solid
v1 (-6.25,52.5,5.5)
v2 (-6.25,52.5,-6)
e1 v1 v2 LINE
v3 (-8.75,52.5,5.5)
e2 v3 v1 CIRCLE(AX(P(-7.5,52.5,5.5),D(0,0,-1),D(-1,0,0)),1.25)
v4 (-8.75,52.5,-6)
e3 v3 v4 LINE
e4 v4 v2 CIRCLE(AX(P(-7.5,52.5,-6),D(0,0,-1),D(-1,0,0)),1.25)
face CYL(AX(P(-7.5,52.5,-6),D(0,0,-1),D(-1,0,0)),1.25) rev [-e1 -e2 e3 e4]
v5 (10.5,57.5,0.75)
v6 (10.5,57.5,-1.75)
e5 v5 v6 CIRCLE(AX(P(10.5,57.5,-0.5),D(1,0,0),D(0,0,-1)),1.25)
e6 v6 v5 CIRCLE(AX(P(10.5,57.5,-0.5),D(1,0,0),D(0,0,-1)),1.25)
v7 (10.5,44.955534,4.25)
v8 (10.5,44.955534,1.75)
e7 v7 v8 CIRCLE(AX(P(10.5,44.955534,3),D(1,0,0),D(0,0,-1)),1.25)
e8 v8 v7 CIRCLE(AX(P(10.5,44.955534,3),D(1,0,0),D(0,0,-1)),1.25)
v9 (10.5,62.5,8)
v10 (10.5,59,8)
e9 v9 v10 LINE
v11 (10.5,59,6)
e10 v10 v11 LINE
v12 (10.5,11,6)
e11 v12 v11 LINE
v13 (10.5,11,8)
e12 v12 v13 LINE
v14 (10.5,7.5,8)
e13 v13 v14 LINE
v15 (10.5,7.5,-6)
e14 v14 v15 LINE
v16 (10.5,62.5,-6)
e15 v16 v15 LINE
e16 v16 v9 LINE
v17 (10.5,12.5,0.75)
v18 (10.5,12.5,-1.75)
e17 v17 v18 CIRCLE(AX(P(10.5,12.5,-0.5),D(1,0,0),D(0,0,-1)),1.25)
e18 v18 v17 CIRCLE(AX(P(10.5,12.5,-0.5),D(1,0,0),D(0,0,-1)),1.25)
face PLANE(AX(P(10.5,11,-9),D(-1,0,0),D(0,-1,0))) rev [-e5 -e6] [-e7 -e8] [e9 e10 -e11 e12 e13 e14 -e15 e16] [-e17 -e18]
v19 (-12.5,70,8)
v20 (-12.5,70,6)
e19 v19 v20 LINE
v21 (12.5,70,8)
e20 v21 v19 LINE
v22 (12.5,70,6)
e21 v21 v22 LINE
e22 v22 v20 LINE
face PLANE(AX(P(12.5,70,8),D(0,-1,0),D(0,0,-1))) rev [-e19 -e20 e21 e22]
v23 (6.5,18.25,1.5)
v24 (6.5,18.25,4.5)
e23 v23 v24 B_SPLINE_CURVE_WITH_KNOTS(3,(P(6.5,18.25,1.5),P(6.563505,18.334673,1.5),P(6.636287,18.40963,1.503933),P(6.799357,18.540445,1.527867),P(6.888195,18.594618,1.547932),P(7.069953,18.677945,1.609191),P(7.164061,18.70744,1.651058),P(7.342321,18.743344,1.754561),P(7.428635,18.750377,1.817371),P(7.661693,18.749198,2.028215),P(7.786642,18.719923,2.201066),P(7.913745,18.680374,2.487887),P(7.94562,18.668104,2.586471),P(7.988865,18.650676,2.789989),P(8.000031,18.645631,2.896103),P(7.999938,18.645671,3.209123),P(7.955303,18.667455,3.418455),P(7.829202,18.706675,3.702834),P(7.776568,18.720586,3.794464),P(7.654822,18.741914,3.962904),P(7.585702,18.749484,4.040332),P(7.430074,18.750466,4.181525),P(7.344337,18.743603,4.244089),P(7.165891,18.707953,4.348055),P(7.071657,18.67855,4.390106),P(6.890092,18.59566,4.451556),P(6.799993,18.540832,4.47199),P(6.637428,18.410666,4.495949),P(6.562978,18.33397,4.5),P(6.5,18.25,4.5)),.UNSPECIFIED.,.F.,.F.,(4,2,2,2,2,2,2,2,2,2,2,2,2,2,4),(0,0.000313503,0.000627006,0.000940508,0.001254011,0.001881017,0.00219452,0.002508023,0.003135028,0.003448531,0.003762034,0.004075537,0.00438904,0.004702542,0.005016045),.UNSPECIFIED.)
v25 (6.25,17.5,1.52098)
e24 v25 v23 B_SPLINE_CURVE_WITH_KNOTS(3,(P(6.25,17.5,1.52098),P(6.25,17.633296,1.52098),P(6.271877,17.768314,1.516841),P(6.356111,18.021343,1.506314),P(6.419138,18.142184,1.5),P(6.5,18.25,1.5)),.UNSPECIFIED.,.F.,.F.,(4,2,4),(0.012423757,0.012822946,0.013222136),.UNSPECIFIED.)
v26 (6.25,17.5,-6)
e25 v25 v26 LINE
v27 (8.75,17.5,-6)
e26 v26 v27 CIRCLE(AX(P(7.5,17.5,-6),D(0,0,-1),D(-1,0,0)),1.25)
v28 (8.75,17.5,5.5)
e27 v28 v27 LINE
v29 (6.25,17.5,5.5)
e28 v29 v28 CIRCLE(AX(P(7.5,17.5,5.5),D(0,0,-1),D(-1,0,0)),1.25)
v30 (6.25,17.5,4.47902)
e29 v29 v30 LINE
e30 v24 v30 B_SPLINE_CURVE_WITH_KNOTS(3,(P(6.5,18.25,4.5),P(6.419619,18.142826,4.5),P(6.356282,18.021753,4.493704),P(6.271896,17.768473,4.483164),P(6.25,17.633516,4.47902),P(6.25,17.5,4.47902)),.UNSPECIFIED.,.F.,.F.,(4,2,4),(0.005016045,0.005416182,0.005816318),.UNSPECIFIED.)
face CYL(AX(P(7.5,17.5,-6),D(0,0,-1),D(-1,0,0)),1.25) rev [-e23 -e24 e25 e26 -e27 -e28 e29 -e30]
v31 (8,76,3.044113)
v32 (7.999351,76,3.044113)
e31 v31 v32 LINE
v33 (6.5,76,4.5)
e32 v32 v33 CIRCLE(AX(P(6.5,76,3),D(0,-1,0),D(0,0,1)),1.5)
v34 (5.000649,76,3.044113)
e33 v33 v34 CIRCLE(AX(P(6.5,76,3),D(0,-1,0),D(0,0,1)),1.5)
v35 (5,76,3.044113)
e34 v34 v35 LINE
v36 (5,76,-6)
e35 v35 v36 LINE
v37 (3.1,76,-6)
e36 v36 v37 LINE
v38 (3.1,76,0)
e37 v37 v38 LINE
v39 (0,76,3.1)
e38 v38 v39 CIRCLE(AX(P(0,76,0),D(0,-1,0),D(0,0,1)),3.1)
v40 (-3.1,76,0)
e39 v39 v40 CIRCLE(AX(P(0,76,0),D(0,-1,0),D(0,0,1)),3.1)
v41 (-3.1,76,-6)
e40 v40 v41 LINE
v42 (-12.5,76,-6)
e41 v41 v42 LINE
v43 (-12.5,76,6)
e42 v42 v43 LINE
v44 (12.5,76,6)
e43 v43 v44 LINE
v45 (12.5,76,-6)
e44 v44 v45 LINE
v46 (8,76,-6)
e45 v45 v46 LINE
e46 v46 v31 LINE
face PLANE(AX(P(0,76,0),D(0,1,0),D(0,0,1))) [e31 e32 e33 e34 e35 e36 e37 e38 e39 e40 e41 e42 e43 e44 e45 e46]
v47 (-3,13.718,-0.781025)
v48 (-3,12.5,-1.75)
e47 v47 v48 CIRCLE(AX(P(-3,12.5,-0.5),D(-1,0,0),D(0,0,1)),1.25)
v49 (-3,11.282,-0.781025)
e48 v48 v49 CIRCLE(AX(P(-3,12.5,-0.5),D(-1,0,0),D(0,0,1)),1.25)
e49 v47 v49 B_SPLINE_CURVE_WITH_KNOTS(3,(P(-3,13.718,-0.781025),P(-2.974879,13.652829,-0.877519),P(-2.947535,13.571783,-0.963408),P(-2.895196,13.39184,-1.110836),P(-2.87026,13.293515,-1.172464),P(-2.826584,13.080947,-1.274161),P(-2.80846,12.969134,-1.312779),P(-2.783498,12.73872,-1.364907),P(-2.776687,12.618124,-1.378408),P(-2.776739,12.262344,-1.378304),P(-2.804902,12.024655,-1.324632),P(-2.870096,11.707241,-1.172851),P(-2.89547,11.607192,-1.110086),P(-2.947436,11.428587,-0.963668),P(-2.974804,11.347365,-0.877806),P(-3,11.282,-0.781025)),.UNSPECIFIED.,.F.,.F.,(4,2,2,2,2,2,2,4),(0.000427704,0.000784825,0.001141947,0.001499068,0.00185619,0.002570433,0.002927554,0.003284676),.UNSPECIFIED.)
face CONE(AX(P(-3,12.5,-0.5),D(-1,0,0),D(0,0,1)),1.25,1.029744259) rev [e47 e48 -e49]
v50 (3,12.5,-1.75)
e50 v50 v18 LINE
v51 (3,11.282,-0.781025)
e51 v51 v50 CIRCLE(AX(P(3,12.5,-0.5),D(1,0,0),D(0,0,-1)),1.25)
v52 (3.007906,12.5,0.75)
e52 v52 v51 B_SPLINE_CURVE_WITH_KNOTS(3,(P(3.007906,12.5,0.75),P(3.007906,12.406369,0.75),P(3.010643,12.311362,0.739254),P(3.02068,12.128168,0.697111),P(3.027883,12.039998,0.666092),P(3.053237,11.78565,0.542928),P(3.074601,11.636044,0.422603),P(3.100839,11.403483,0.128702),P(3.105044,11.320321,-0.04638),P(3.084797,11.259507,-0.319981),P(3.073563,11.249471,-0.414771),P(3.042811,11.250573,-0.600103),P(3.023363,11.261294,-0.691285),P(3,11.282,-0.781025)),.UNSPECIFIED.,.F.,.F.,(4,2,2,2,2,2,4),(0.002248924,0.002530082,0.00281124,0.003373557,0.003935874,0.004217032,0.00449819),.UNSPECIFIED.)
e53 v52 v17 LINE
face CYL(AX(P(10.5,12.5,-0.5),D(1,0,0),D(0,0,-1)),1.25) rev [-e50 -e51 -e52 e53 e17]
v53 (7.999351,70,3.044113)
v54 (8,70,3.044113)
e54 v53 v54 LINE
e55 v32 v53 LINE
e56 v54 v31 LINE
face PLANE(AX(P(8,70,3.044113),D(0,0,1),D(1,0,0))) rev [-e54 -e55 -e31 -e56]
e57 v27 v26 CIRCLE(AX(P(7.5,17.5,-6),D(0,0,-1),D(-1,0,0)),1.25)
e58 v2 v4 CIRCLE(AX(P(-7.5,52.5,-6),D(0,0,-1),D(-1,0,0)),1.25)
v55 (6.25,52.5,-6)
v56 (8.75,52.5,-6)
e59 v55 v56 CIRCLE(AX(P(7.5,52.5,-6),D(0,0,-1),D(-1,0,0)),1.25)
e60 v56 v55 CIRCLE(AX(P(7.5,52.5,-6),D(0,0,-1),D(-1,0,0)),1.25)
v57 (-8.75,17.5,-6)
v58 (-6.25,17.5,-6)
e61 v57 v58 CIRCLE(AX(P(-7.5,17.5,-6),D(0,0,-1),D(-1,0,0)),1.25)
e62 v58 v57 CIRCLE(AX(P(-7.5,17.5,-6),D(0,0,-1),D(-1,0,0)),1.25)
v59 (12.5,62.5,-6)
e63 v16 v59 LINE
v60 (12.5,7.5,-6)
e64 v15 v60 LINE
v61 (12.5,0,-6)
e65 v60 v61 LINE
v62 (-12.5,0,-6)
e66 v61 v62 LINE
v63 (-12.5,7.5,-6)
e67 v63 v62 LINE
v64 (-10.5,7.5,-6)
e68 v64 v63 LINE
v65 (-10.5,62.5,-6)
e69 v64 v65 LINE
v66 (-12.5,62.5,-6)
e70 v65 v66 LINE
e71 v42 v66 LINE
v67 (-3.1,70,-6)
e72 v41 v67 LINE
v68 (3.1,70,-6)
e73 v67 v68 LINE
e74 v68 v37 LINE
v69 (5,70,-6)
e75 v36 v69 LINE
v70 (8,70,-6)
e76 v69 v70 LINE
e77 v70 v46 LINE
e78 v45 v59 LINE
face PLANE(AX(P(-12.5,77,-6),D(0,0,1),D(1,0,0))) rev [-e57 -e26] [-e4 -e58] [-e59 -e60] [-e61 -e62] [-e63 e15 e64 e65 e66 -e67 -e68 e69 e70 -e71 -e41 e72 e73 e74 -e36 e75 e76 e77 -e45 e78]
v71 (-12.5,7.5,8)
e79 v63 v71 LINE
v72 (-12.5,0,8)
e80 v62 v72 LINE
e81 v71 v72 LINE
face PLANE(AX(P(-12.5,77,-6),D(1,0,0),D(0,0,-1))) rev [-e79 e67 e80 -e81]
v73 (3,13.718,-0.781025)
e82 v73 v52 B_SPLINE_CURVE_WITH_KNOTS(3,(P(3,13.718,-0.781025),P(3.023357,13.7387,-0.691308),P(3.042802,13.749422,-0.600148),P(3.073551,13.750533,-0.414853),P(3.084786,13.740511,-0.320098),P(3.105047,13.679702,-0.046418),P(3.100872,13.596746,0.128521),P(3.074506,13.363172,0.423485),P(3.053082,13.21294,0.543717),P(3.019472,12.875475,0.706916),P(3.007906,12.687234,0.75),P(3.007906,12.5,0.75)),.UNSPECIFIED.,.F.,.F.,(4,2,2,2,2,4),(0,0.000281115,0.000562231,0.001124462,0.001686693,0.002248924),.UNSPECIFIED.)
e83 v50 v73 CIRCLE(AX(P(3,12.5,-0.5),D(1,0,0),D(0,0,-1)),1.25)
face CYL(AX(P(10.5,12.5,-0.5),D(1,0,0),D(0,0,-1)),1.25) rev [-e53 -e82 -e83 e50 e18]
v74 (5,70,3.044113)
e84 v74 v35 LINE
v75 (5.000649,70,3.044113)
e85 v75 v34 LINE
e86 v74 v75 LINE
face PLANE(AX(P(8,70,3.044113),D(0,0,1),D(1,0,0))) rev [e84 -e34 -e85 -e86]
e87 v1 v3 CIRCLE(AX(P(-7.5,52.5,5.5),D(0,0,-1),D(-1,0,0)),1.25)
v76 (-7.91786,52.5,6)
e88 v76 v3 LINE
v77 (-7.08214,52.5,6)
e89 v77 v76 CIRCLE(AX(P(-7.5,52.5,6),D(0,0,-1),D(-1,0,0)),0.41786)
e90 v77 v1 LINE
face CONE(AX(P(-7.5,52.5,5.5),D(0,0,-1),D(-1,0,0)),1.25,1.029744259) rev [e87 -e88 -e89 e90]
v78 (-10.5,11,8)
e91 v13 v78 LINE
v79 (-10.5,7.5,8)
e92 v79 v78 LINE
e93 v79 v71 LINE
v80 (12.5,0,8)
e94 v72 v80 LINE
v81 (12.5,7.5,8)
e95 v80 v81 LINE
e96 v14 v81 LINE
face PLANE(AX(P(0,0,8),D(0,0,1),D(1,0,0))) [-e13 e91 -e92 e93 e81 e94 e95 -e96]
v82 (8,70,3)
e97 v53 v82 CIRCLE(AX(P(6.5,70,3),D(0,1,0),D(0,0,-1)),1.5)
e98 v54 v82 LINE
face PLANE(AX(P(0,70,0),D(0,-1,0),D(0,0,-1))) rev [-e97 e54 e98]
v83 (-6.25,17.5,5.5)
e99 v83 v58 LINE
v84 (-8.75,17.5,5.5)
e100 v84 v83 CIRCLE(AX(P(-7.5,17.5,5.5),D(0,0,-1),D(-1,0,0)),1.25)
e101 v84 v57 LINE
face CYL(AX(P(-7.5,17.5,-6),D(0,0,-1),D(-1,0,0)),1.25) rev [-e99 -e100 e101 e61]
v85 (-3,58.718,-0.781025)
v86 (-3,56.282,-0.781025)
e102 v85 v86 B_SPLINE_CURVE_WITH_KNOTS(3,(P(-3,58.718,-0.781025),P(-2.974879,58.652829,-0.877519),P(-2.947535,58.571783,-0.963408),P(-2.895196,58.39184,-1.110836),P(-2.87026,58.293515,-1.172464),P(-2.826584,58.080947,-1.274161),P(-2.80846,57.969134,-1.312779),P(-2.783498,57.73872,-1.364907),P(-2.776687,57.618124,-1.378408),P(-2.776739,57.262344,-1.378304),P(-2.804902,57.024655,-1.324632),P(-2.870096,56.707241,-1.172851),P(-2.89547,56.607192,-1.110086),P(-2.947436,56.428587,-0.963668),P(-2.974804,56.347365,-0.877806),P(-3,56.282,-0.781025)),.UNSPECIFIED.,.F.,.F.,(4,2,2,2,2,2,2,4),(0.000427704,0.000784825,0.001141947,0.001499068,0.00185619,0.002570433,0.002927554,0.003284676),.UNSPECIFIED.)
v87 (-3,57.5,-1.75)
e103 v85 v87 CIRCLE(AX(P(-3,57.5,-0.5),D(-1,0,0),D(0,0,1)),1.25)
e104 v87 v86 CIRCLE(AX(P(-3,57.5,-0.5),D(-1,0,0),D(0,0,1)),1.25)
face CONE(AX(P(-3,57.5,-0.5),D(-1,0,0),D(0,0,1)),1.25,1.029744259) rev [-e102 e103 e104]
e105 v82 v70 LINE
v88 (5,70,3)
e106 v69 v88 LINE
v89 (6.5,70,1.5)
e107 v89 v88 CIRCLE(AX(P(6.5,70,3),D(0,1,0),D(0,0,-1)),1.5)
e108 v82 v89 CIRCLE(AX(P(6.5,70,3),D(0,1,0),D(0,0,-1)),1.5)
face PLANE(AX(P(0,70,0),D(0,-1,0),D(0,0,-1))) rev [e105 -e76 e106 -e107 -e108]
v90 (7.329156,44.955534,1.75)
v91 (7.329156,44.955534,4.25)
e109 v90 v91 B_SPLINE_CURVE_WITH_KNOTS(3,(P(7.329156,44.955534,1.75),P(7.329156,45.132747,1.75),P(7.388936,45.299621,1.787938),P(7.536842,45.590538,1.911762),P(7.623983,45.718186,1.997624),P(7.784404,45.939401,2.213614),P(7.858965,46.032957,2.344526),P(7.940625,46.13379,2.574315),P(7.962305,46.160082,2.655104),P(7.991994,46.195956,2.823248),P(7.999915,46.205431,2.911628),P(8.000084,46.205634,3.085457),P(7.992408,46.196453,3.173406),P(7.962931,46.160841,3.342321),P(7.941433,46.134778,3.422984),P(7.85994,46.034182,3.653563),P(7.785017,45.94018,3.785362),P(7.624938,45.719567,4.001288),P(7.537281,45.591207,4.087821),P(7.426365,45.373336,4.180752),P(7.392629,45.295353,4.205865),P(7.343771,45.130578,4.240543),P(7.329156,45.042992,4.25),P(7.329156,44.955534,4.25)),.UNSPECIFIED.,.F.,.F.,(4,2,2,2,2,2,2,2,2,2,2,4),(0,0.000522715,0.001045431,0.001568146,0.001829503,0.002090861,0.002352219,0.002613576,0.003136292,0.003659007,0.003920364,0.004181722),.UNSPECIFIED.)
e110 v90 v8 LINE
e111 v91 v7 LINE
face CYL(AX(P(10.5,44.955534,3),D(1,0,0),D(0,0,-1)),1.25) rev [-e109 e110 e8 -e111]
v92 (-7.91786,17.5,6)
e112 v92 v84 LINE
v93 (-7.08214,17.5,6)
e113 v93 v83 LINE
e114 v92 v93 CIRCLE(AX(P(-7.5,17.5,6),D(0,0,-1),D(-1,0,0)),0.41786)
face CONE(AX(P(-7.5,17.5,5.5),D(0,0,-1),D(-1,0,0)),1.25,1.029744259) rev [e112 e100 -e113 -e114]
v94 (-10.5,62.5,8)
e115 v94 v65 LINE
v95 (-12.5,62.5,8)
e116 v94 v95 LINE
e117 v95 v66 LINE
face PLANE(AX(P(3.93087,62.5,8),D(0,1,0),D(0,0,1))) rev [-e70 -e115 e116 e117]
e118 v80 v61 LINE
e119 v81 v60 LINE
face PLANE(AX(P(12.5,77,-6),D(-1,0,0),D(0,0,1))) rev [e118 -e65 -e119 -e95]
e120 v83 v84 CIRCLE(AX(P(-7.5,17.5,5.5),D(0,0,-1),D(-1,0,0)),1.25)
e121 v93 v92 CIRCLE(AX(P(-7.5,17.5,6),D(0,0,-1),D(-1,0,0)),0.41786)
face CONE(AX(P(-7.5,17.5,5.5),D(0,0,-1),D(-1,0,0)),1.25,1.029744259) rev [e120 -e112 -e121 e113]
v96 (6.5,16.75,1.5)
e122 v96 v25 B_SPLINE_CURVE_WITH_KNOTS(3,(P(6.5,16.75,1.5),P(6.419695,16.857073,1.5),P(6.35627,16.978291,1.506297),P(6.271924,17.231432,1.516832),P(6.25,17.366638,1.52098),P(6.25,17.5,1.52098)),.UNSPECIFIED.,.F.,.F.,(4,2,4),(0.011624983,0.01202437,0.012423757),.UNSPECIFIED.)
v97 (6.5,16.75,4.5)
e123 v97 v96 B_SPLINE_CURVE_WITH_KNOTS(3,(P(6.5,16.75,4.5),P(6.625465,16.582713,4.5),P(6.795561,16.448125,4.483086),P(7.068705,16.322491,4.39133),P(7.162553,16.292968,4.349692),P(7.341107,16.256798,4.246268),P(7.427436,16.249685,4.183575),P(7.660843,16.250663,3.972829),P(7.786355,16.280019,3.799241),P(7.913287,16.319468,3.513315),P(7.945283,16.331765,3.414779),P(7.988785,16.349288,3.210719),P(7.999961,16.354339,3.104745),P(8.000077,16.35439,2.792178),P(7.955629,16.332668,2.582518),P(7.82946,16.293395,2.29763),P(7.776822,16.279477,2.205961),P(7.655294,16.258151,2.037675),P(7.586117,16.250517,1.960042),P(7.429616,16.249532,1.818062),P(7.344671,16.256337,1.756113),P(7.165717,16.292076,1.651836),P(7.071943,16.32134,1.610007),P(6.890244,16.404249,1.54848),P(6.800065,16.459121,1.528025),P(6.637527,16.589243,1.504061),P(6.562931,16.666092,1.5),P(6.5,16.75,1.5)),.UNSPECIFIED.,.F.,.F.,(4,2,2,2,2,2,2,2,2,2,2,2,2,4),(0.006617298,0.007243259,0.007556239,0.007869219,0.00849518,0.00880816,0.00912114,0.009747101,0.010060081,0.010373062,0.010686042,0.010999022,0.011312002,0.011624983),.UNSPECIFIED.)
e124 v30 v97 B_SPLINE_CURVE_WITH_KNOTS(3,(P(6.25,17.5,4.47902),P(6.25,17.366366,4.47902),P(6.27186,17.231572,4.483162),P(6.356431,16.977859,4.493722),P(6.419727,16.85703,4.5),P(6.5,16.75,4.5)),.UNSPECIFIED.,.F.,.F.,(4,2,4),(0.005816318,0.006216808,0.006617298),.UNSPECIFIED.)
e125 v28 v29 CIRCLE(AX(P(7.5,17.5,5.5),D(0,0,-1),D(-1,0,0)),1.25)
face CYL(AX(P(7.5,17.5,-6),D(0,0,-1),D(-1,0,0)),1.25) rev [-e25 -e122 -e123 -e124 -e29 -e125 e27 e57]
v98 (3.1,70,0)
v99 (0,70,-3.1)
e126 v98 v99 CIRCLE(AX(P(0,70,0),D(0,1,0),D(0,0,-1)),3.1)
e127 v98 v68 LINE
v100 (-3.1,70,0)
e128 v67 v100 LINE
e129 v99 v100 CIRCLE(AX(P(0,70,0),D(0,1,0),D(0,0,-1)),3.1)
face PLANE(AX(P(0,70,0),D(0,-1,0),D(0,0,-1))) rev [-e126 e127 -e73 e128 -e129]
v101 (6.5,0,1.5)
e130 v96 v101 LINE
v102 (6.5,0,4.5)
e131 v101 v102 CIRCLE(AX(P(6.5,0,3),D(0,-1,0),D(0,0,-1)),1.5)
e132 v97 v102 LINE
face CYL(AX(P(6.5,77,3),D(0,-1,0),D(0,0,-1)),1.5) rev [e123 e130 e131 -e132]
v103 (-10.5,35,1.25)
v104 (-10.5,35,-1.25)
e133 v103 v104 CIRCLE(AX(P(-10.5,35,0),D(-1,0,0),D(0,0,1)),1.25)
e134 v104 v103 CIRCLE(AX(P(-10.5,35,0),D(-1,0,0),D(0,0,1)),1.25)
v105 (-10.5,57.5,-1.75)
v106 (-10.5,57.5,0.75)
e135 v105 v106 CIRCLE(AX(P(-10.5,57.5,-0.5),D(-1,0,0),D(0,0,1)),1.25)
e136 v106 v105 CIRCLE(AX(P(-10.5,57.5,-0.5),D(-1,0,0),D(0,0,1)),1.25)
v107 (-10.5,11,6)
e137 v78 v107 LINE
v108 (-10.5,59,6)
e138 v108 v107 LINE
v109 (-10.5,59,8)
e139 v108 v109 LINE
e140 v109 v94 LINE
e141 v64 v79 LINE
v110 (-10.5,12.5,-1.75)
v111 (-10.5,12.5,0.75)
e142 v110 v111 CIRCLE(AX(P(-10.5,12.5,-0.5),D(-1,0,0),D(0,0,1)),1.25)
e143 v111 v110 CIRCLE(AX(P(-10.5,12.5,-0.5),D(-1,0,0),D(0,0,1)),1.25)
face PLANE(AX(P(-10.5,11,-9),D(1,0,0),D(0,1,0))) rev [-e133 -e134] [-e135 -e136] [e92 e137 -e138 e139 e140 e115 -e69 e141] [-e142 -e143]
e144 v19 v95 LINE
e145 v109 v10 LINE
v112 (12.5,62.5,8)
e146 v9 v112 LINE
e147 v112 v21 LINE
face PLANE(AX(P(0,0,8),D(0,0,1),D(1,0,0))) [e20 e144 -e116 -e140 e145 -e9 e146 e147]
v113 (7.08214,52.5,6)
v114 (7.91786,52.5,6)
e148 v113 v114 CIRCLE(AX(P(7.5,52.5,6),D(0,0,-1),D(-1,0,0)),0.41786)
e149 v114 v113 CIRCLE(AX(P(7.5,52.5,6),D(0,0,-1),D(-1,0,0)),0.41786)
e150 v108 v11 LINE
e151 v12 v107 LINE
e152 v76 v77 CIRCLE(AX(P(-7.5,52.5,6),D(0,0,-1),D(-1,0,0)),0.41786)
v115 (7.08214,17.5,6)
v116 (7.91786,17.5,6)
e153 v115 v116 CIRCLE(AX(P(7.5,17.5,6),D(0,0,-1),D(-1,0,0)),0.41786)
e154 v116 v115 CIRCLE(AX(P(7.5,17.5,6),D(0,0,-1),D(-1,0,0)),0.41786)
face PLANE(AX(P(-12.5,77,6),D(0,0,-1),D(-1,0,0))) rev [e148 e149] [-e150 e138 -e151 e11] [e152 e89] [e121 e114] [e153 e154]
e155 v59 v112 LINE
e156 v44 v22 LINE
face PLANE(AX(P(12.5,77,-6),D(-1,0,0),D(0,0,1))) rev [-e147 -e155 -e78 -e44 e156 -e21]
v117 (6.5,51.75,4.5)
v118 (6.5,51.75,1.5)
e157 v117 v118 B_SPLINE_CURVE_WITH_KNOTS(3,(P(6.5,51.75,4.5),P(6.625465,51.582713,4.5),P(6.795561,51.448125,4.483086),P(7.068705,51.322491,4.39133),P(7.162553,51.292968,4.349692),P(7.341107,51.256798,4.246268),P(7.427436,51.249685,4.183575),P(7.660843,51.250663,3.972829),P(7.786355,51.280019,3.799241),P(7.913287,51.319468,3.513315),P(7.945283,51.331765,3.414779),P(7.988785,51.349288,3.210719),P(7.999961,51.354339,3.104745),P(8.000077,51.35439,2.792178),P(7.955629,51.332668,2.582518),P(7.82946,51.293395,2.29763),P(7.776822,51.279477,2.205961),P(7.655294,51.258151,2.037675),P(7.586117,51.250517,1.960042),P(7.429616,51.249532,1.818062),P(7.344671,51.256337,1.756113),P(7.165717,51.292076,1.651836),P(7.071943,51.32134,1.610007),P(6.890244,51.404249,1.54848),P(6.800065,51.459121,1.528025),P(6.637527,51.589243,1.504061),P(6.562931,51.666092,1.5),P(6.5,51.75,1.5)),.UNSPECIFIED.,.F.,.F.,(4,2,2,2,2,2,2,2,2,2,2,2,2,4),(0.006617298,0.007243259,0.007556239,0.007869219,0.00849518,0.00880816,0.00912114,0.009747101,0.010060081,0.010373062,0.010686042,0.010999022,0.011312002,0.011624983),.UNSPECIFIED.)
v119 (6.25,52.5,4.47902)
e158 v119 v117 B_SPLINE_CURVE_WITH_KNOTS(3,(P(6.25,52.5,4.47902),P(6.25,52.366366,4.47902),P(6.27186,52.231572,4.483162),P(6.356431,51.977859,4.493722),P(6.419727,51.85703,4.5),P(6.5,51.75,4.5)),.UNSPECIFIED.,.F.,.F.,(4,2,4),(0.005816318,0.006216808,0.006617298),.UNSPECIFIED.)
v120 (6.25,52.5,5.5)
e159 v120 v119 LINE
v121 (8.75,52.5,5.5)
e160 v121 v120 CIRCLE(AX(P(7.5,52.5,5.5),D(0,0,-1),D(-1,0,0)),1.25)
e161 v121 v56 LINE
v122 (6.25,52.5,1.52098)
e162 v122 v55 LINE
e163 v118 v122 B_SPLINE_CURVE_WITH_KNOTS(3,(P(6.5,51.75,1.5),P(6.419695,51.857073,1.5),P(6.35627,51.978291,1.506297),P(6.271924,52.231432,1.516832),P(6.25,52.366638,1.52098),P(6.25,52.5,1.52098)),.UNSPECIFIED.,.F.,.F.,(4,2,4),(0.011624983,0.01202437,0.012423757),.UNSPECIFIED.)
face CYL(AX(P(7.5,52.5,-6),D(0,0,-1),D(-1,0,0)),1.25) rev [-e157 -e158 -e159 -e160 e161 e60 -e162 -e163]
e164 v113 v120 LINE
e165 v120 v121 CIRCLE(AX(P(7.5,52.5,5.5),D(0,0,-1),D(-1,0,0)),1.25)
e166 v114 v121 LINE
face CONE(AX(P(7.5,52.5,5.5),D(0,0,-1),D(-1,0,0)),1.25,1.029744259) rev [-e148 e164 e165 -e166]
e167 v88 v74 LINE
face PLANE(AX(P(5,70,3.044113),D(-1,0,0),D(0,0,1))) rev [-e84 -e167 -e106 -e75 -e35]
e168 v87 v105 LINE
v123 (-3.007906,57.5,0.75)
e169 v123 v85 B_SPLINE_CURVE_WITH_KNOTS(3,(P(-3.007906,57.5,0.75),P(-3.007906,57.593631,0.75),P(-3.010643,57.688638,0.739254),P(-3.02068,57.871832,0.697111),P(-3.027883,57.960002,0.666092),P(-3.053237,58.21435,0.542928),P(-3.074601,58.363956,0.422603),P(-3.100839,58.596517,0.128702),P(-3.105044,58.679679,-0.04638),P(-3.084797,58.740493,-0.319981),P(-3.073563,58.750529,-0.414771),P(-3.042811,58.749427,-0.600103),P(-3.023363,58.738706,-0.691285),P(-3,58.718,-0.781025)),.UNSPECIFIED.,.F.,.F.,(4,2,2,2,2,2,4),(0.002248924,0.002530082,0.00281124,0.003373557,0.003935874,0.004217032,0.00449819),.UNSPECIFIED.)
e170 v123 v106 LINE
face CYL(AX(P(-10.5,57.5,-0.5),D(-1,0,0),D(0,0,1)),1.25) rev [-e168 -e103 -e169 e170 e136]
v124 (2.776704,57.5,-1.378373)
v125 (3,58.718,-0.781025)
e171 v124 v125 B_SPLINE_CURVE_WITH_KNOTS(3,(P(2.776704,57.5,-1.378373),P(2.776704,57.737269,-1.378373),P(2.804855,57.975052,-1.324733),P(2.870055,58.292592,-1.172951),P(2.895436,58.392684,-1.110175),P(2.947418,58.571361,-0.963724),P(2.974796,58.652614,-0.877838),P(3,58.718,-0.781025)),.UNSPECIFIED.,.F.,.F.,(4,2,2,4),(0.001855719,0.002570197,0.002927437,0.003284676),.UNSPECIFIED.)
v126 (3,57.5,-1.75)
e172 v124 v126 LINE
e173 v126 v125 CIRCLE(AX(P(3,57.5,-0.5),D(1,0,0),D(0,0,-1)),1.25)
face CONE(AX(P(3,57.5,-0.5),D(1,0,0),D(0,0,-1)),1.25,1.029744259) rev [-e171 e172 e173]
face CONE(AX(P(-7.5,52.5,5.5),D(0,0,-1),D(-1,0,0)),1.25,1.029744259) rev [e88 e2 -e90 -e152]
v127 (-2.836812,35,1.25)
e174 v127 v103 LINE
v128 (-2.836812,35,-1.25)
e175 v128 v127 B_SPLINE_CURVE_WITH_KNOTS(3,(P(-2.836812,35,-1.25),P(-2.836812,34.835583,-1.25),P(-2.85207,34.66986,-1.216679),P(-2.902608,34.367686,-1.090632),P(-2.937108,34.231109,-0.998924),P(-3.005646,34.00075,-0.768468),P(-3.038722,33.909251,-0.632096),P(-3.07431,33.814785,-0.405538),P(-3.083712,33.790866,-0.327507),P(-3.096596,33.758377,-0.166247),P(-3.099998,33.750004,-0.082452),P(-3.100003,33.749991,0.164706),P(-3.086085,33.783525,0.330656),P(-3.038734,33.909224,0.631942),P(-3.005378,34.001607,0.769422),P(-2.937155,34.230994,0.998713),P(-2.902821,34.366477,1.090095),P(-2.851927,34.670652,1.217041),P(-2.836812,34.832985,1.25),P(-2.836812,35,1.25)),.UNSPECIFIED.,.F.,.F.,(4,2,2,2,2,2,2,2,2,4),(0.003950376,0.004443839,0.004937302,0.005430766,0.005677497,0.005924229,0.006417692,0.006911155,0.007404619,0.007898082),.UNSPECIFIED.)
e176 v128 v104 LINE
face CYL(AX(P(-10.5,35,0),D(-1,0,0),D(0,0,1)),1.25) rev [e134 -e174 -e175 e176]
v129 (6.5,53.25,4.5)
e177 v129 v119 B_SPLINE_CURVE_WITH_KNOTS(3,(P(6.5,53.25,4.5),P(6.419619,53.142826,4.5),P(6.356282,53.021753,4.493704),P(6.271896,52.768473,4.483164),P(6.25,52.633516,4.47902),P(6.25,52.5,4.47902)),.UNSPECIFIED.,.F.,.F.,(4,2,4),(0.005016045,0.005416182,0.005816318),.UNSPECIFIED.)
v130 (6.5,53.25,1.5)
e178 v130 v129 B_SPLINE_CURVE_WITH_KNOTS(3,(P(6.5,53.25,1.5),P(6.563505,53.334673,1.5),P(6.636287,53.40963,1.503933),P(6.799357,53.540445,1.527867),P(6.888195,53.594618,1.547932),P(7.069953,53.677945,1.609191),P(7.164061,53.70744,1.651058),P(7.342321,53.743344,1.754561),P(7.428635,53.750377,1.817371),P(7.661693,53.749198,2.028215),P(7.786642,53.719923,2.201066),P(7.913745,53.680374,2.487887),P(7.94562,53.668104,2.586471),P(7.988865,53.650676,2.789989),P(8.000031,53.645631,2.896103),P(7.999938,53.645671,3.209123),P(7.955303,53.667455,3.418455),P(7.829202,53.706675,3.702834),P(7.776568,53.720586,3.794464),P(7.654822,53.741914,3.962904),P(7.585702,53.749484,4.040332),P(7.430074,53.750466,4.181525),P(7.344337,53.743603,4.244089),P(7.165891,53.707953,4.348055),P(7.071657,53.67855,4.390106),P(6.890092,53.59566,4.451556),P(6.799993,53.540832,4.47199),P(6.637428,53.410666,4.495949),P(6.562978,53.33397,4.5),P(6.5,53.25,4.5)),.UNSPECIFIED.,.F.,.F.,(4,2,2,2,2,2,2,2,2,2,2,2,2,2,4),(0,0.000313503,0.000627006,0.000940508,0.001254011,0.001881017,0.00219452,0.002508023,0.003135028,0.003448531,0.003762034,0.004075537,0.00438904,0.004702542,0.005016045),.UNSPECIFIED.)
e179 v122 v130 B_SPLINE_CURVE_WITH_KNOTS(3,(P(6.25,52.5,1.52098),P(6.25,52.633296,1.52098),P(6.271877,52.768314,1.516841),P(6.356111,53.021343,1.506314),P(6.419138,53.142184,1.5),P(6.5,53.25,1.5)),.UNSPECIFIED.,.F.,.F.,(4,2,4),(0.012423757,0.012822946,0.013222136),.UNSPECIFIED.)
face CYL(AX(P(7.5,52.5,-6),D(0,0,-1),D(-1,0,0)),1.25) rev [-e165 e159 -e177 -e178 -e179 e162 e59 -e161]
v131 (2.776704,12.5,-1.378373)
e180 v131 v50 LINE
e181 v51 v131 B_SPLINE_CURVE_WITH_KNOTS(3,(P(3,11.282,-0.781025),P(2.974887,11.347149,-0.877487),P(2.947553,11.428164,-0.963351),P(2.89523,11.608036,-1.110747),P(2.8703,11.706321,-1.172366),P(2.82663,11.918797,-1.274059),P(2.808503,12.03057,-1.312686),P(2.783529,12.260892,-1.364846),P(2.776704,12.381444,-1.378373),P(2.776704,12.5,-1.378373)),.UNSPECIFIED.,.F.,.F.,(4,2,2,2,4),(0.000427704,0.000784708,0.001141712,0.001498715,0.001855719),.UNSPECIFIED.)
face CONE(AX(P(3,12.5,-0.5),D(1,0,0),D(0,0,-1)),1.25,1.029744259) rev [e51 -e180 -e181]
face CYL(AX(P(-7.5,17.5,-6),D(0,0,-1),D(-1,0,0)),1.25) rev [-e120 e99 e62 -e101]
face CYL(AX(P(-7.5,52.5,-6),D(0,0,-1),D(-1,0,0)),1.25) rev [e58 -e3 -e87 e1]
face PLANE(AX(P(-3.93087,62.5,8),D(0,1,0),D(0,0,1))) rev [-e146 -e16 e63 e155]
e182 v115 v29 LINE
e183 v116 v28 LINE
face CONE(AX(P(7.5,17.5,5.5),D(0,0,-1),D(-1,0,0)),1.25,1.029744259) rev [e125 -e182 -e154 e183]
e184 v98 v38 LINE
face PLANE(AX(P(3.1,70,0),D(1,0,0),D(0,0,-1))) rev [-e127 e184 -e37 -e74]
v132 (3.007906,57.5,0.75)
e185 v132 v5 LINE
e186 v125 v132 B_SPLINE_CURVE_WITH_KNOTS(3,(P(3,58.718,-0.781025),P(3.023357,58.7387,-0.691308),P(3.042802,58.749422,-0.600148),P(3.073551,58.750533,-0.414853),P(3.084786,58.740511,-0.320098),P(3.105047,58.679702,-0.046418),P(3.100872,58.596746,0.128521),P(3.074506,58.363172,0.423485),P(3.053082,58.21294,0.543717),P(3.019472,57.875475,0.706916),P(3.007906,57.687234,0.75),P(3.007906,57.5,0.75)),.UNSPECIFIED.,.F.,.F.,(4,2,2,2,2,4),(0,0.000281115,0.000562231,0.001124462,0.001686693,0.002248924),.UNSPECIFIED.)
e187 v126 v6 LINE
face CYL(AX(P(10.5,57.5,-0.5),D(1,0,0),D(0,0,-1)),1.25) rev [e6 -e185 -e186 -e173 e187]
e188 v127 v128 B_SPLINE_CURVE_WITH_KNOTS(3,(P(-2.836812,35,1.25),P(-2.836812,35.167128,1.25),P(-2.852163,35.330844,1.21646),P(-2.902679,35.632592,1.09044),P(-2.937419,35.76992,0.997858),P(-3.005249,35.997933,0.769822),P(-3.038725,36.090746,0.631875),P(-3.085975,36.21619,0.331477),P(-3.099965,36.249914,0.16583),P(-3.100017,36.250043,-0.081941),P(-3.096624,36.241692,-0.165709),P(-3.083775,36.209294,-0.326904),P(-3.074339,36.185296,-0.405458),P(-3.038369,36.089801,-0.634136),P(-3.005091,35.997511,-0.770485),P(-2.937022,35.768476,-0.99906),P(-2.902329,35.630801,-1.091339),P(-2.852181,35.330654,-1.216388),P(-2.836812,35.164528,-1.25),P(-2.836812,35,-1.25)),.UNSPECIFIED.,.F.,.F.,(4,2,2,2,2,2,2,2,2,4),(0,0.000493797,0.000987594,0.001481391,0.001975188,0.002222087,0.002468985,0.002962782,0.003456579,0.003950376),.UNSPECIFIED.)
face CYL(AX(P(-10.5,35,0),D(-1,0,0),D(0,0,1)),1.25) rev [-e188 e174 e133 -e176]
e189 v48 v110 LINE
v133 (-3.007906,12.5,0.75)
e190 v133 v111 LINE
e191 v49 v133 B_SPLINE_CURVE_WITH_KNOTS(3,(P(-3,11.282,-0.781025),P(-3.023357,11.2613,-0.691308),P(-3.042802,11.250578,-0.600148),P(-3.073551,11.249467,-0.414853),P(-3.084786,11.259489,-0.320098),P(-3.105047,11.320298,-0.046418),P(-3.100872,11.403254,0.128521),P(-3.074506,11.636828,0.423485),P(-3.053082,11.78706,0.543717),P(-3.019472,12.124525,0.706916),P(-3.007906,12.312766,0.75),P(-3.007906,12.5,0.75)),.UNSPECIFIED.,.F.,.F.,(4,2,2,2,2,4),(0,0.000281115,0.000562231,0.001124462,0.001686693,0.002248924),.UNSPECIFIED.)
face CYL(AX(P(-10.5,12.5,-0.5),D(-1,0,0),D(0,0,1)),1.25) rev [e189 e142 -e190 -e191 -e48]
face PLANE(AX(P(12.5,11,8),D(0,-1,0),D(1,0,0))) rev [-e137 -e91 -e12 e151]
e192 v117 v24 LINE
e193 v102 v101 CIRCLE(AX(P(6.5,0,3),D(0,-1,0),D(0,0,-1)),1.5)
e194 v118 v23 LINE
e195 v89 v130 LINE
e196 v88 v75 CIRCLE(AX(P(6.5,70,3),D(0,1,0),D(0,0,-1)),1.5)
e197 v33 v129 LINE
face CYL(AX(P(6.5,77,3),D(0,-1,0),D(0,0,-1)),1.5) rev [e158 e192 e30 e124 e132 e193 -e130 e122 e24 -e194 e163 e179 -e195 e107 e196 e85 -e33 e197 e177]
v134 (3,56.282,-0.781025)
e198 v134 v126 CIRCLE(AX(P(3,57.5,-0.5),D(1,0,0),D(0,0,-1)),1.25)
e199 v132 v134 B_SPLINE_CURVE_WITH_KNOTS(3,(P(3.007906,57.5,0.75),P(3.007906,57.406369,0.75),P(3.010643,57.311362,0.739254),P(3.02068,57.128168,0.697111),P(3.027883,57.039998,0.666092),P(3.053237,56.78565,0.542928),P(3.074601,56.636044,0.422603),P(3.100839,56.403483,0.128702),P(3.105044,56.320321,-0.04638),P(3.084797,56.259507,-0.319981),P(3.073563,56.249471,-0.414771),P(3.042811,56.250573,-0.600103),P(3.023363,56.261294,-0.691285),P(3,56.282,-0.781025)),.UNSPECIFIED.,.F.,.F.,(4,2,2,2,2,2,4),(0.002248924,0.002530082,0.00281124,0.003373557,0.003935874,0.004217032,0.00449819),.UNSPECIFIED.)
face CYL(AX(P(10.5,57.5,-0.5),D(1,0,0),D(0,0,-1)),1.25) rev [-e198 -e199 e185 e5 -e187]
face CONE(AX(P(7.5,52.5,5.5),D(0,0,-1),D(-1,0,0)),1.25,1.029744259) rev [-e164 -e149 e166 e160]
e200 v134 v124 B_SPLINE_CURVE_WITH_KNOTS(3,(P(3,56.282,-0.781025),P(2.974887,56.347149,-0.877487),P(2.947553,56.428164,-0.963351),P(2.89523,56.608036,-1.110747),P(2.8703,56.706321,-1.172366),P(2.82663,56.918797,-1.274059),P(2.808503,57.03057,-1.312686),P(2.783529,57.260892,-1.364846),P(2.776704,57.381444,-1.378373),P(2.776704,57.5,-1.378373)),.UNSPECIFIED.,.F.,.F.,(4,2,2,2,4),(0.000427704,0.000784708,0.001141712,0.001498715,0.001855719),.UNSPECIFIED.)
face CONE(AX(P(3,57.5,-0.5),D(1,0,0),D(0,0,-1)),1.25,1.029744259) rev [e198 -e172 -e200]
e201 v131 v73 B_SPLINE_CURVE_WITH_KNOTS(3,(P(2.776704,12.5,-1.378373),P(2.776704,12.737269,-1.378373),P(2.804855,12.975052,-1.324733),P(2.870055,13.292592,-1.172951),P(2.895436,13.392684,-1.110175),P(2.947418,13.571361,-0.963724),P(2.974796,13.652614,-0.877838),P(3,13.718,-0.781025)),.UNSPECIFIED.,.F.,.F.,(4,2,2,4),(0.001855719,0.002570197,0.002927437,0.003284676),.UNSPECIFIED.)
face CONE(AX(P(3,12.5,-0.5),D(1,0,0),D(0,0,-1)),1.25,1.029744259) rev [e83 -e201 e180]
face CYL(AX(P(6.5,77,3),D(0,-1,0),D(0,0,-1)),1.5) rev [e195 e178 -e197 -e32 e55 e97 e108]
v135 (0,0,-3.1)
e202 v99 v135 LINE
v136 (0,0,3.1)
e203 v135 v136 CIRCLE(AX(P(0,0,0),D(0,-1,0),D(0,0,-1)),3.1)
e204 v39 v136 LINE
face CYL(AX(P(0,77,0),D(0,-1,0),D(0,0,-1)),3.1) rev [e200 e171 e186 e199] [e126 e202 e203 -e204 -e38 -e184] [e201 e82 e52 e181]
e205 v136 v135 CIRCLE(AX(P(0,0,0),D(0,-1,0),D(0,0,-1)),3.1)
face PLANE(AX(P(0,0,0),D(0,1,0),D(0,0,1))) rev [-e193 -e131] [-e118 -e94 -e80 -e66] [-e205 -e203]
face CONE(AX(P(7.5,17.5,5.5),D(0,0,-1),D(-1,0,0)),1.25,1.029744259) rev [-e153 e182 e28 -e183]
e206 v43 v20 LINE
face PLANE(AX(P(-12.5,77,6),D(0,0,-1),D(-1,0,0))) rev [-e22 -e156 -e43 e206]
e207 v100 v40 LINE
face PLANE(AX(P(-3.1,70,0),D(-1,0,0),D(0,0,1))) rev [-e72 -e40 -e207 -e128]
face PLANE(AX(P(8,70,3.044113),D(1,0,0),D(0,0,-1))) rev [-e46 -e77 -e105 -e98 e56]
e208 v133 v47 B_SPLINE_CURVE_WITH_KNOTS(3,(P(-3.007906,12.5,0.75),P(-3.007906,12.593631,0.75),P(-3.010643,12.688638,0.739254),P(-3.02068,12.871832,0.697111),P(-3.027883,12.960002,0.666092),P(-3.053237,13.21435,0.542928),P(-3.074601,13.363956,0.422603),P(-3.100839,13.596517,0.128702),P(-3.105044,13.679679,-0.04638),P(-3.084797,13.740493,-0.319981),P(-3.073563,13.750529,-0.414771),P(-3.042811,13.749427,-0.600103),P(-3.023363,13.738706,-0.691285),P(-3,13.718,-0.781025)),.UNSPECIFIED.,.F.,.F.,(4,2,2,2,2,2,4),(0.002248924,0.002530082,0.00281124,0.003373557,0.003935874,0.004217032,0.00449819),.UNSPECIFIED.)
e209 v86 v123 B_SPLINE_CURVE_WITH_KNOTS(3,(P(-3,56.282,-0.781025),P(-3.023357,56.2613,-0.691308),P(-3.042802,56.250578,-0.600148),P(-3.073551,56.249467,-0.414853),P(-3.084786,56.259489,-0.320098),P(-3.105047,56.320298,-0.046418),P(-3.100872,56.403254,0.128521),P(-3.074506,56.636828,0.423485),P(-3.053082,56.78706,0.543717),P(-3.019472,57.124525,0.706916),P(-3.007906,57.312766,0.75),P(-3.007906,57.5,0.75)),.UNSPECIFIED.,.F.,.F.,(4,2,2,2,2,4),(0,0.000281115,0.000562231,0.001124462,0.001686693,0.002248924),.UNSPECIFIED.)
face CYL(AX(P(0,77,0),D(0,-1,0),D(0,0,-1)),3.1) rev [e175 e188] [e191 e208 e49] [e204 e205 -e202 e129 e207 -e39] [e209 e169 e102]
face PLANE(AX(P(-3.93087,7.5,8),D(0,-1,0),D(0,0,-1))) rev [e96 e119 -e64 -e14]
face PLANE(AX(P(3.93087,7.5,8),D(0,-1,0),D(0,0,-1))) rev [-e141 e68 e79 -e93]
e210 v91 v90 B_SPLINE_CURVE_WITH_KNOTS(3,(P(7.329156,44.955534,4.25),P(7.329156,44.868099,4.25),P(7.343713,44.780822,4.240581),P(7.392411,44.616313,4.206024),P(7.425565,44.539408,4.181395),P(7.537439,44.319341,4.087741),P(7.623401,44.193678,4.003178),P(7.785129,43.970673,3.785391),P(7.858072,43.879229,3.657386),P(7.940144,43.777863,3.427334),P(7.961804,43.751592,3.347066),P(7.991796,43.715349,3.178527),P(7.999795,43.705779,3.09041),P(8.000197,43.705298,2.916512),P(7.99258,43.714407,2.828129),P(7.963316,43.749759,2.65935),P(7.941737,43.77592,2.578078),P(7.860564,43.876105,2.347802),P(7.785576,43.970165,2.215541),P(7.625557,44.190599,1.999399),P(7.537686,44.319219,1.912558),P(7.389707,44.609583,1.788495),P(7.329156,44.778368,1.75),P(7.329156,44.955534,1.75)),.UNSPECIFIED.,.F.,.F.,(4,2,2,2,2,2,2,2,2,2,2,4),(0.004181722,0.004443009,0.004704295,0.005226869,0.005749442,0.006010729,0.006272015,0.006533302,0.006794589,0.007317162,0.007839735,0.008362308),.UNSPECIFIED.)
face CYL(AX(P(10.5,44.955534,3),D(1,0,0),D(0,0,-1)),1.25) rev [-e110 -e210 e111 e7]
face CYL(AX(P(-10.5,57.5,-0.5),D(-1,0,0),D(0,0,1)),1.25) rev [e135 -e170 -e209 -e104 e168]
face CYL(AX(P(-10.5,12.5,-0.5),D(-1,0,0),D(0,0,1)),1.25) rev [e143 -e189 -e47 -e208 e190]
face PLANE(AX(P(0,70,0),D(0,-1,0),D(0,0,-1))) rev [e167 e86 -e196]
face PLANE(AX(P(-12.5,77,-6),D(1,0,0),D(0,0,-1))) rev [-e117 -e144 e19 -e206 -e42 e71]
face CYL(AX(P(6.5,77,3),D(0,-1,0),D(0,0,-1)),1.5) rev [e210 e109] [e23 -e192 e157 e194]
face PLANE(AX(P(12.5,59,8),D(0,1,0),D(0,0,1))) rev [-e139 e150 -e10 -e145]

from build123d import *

# Parameters (mm, degrees)
SKETCH1_W                  = 25
SKETCH1_H                  = 12
BOSS_EXTRUDE1_DEPTH        = 77
SKETCH2_R                  = 3.1
SKETCH2_R_2                = 1.5
CUT_EXTRUDE1_DEPTH         = 79.238417673
SKETCH4_W                  = 6.2
SKETCH4_H                  = 12
SKETCH4_W_2                = 3
SKETCH4_H_2                = 18.04411339
CUT_EXTRUDE3_DEPTH         = 7
SKETCH5_W                  = 25
SKETCH5_H                  = 11
BOSS_EXTRUDE2_DEPTH        = 2
SKETCH6_W                  = 2
SKETCH6_H                  = 48
CUT_EXTRUDE4_DEPTH         = 17
M3_TAPPED_HOLE1_AT_2_COUNT = 2
M3_TAPPED_HOLE1_AT_2_PITCH = 45
M3_TAPPED_HOLE2_D          = 2.5
M3_TAPPED_HOLE2_DEPTH      = 11.5
M3_TAPPED_HOLE2_TIP        = 0.751075774
SKETCH13_W                 = 14
SKETCH13_H                 = 3.5
CUT_EXTRUDE5_DEPTH         = 2
SKETCH14_W                 = 14
SKETCH14_H                 = 3.5
CUT_EXTRUDE6_DEPTH         = 2
M3_TAPPED_HOLE3_D          = 2.5
M3_TAPPED_HOLE3_DEPTH      = 4.5
M3_TAPPED_HOLE3_TIP        = 0.751075774
SKETCH20_W                 = 25
SKETCH20_H                 = 14
CUT_EXTRUDE9_DEPTH         = 1
M3_TAPPED_HOLE5_D          = 2.5
M3_TAPPED_HOLE5_DEPTH      = 9
M3_TAPPED_HOLE5_TIP        = 0.751075774


with BuildPart() as part:
    # Sketch1 → Boss-Extrude1 (new body)
    with BuildSketch(Plane(origin=(0, 0, 0), x_dir=(1, 0, 0), z_dir=(0, 1, 0))):
        Rectangle(SKETCH1_W, SKETCH1_H)
    extrude(amount=BOSS_EXTRUDE1_DEPTH)

    # Sketch2 → Cut-Extrude1 (cut, through all)
    with BuildSketch(Plane.XZ):
        with Locations(Location((0, 0, 0), (0, 0, 270))):
            Circle(SKETCH2_R)
        with Locations(Location((6.5, 3, 0), (0, 0, 270))):
            Circle(SKETCH2_R_2)
    extrude(amount=-CUT_EXTRUDE1_DEPTH, mode=Mode.SUBTRACT)

    # Sketch4 → Cut-Extrude3 (cut)
    with BuildSketch(Plane(origin=(0, 77, 0), x_dir=(1, 0, 0), z_dir=(0, 1, 0))):
        with Locations((0, 6)):
            Rectangle(SKETCH4_W, SKETCH4_H)
        with Locations((6.5, 5.977943305)):
            Rectangle(SKETCH4_W_2, SKETCH4_H_2)
    extrude(amount=-CUT_EXTRUDE3_DEPTH, mode=Mode.SUBTRACT)

    # Sketch5 → Boss-Extrude2 (add)
    with BuildSketch(Plane.XY.offset(6)):
        with Locations((0, 5.5)):
            Rectangle(SKETCH5_W, SKETCH5_H)
        with Locations((0, 64.5)):
            Rectangle(SKETCH5_W, SKETCH5_H)
    extrude(amount=BOSS_EXTRUDE2_DEPTH)

    # Sketch6 → Cut-Extrude4 (cut)
    with BuildSketch(Plane.XY.offset(8)):
        with Locations((11.5, 35)):
            Rectangle(SKETCH6_W, SKETCH6_H)
        with Locations((-11.5, 35)):
            Rectangle(SKETCH6_W, SKETCH6_H)
    extrude(amount=-CUT_EXTRUDE4_DEPTH, mode=Mode.SUBTRACT)

    # Sketch8 → M3 Tapped Hole1 (revolve, cut)
    with BuildSketch(Plane(origin=(10.5, 57.5, -0.5), x_dir=(0, 0, -1), z_dir=(0, 1, 0))):
        Polygon((0, 0), (0, 8.251075774), (1.25, 7.5), (1.25, 0), align=None)
    m3_tapped_hole1 = revolve(axis=Axis((16.85, 57.5, -0.5), (-1, 0, 0)), mode=Mode.SUBTRACT)

    # M3 Tapped Hole1 at 2: M3 Tapped Hole1 ×2
    with Locations(*[(0, -i * M3_TAPPED_HOLE1_AT_2_PITCH, 0) for i in range(1, M3_TAPPED_HOLE1_AT_2_COUNT)]):
        add(m3_tapped_hole1, mode=Mode.SUBTRACT)

    # Mirror1: M3 Tapped Hole1 across plane
    add(m3_tapped_hole1.mirror(Plane(origin=(0, 0, 0), x_dir=(0, 0, 1), z_dir=(1, 0, 0))), mode=Mode.SUBTRACT)

    # Mirror1 copy 1 sketch → Mirror1 copy 1 (revolve, cut)
    with BuildSketch(Plane(origin=(-10.5, 12.5, -0.5), x_dir=(0, 0, -1), z_dir=(0, 1, 0))):
        Polygon((0, 0), (0, -8.251075774), (1.25, -7.5), (1.25, 0), align=None)
    revolve(axis=Axis((-16.85, 12.5, -0.5), (-1, 0, 0)), mode=Mode.SUBTRACT)

    # M3 Tapped Hole2
    with Locations(Plane(origin=(-7.5, 52.5, -6), x_dir=(-1, 0, 0), z_dir=(0, 0, -1))):
        with Locations((0, 0), (-15, 0), (-15, -35), (0, -35)):
            Hole(M3_TAPPED_HOLE2_D / 2, depth=M3_TAPPED_HOLE2_DEPTH)
            with Locations((0, 0, -(M3_TAPPED_HOLE2_DEPTH + M3_TAPPED_HOLE2_TIP / 2))):  # 118° drill point
                Cone(0, M3_TAPPED_HOLE2_D / 2, M3_TAPPED_HOLE2_TIP, mode=Mode.SUBTRACT)

    # Sketch13 → Cut-Extrude5 (cut)
    with BuildSketch(Plane(origin=(12.5, 0, 0), x_dir=(0, 0, -1), z_dir=(1, 0, 0))):
        with Locations((-1, 60.75)):
            Rectangle(SKETCH13_W, SKETCH13_H)
        with Locations((-1, 9.25)):
            Rectangle(SKETCH13_W, SKETCH13_H)
    extrude(amount=-CUT_EXTRUDE5_DEPTH, mode=Mode.SUBTRACT)

    # Sketch14 → Cut-Extrude6 (cut)
    with BuildSketch(Plane.ZY.offset(12.5)):
        with Locations((1, 60.75)):
            Rectangle(SKETCH14_W, SKETCH14_H)
        with Locations((1, 9.25)):
            Rectangle(SKETCH14_W, SKETCH14_H)
    extrude(amount=-CUT_EXTRUDE6_DEPTH, mode=Mode.SUBTRACT)

    # M3 Tapped Hole3
    with Locations(Plane(origin=(10.5, 44.955533586, 3), x_dir=(0, 1, 0), z_dir=(1, 0, 0))):
        with Locations((0, 0)):
            Hole(M3_TAPPED_HOLE3_D / 2, depth=M3_TAPPED_HOLE3_DEPTH)
            with Locations((0, 0, -(M3_TAPPED_HOLE3_DEPTH + M3_TAPPED_HOLE3_TIP / 2))):  # 118° drill point
                Cone(0, M3_TAPPED_HOLE3_D / 2, M3_TAPPED_HOLE3_TIP, mode=Mode.SUBTRACT)

    # Sketch20 → Cut-Extrude9 (cut)
    with BuildSketch(Plane(origin=(0, 77, 0), x_dir=(1, 0, 0), z_dir=(0, 1, 0))):
        with Locations((0, -1)):
            Rectangle(SKETCH20_W, SKETCH20_H)
    extrude(amount=-CUT_EXTRUDE9_DEPTH, mode=Mode.SUBTRACT)

    # M3 Tapped Hole5
    with Locations(Plane(origin=(-10.5, 35, 0), x_dir=(0, -1, 0), z_dir=(-1, 0, 0))):
        with Locations((0, 0)):
            Hole(M3_TAPPED_HOLE5_D / 2, depth=M3_TAPPED_HOLE5_DEPTH)
            with Locations((0, 0, -(M3_TAPPED_HOLE5_DEPTH + M3_TAPPED_HOLE5_TIP / 2))):  # 118° drill point
                Cone(0, M3_TAPPED_HOLE5_D / 2, M3_TAPPED_HOLE5_TIP, mode=Mode.SUBTRACT)


solid = part.part
